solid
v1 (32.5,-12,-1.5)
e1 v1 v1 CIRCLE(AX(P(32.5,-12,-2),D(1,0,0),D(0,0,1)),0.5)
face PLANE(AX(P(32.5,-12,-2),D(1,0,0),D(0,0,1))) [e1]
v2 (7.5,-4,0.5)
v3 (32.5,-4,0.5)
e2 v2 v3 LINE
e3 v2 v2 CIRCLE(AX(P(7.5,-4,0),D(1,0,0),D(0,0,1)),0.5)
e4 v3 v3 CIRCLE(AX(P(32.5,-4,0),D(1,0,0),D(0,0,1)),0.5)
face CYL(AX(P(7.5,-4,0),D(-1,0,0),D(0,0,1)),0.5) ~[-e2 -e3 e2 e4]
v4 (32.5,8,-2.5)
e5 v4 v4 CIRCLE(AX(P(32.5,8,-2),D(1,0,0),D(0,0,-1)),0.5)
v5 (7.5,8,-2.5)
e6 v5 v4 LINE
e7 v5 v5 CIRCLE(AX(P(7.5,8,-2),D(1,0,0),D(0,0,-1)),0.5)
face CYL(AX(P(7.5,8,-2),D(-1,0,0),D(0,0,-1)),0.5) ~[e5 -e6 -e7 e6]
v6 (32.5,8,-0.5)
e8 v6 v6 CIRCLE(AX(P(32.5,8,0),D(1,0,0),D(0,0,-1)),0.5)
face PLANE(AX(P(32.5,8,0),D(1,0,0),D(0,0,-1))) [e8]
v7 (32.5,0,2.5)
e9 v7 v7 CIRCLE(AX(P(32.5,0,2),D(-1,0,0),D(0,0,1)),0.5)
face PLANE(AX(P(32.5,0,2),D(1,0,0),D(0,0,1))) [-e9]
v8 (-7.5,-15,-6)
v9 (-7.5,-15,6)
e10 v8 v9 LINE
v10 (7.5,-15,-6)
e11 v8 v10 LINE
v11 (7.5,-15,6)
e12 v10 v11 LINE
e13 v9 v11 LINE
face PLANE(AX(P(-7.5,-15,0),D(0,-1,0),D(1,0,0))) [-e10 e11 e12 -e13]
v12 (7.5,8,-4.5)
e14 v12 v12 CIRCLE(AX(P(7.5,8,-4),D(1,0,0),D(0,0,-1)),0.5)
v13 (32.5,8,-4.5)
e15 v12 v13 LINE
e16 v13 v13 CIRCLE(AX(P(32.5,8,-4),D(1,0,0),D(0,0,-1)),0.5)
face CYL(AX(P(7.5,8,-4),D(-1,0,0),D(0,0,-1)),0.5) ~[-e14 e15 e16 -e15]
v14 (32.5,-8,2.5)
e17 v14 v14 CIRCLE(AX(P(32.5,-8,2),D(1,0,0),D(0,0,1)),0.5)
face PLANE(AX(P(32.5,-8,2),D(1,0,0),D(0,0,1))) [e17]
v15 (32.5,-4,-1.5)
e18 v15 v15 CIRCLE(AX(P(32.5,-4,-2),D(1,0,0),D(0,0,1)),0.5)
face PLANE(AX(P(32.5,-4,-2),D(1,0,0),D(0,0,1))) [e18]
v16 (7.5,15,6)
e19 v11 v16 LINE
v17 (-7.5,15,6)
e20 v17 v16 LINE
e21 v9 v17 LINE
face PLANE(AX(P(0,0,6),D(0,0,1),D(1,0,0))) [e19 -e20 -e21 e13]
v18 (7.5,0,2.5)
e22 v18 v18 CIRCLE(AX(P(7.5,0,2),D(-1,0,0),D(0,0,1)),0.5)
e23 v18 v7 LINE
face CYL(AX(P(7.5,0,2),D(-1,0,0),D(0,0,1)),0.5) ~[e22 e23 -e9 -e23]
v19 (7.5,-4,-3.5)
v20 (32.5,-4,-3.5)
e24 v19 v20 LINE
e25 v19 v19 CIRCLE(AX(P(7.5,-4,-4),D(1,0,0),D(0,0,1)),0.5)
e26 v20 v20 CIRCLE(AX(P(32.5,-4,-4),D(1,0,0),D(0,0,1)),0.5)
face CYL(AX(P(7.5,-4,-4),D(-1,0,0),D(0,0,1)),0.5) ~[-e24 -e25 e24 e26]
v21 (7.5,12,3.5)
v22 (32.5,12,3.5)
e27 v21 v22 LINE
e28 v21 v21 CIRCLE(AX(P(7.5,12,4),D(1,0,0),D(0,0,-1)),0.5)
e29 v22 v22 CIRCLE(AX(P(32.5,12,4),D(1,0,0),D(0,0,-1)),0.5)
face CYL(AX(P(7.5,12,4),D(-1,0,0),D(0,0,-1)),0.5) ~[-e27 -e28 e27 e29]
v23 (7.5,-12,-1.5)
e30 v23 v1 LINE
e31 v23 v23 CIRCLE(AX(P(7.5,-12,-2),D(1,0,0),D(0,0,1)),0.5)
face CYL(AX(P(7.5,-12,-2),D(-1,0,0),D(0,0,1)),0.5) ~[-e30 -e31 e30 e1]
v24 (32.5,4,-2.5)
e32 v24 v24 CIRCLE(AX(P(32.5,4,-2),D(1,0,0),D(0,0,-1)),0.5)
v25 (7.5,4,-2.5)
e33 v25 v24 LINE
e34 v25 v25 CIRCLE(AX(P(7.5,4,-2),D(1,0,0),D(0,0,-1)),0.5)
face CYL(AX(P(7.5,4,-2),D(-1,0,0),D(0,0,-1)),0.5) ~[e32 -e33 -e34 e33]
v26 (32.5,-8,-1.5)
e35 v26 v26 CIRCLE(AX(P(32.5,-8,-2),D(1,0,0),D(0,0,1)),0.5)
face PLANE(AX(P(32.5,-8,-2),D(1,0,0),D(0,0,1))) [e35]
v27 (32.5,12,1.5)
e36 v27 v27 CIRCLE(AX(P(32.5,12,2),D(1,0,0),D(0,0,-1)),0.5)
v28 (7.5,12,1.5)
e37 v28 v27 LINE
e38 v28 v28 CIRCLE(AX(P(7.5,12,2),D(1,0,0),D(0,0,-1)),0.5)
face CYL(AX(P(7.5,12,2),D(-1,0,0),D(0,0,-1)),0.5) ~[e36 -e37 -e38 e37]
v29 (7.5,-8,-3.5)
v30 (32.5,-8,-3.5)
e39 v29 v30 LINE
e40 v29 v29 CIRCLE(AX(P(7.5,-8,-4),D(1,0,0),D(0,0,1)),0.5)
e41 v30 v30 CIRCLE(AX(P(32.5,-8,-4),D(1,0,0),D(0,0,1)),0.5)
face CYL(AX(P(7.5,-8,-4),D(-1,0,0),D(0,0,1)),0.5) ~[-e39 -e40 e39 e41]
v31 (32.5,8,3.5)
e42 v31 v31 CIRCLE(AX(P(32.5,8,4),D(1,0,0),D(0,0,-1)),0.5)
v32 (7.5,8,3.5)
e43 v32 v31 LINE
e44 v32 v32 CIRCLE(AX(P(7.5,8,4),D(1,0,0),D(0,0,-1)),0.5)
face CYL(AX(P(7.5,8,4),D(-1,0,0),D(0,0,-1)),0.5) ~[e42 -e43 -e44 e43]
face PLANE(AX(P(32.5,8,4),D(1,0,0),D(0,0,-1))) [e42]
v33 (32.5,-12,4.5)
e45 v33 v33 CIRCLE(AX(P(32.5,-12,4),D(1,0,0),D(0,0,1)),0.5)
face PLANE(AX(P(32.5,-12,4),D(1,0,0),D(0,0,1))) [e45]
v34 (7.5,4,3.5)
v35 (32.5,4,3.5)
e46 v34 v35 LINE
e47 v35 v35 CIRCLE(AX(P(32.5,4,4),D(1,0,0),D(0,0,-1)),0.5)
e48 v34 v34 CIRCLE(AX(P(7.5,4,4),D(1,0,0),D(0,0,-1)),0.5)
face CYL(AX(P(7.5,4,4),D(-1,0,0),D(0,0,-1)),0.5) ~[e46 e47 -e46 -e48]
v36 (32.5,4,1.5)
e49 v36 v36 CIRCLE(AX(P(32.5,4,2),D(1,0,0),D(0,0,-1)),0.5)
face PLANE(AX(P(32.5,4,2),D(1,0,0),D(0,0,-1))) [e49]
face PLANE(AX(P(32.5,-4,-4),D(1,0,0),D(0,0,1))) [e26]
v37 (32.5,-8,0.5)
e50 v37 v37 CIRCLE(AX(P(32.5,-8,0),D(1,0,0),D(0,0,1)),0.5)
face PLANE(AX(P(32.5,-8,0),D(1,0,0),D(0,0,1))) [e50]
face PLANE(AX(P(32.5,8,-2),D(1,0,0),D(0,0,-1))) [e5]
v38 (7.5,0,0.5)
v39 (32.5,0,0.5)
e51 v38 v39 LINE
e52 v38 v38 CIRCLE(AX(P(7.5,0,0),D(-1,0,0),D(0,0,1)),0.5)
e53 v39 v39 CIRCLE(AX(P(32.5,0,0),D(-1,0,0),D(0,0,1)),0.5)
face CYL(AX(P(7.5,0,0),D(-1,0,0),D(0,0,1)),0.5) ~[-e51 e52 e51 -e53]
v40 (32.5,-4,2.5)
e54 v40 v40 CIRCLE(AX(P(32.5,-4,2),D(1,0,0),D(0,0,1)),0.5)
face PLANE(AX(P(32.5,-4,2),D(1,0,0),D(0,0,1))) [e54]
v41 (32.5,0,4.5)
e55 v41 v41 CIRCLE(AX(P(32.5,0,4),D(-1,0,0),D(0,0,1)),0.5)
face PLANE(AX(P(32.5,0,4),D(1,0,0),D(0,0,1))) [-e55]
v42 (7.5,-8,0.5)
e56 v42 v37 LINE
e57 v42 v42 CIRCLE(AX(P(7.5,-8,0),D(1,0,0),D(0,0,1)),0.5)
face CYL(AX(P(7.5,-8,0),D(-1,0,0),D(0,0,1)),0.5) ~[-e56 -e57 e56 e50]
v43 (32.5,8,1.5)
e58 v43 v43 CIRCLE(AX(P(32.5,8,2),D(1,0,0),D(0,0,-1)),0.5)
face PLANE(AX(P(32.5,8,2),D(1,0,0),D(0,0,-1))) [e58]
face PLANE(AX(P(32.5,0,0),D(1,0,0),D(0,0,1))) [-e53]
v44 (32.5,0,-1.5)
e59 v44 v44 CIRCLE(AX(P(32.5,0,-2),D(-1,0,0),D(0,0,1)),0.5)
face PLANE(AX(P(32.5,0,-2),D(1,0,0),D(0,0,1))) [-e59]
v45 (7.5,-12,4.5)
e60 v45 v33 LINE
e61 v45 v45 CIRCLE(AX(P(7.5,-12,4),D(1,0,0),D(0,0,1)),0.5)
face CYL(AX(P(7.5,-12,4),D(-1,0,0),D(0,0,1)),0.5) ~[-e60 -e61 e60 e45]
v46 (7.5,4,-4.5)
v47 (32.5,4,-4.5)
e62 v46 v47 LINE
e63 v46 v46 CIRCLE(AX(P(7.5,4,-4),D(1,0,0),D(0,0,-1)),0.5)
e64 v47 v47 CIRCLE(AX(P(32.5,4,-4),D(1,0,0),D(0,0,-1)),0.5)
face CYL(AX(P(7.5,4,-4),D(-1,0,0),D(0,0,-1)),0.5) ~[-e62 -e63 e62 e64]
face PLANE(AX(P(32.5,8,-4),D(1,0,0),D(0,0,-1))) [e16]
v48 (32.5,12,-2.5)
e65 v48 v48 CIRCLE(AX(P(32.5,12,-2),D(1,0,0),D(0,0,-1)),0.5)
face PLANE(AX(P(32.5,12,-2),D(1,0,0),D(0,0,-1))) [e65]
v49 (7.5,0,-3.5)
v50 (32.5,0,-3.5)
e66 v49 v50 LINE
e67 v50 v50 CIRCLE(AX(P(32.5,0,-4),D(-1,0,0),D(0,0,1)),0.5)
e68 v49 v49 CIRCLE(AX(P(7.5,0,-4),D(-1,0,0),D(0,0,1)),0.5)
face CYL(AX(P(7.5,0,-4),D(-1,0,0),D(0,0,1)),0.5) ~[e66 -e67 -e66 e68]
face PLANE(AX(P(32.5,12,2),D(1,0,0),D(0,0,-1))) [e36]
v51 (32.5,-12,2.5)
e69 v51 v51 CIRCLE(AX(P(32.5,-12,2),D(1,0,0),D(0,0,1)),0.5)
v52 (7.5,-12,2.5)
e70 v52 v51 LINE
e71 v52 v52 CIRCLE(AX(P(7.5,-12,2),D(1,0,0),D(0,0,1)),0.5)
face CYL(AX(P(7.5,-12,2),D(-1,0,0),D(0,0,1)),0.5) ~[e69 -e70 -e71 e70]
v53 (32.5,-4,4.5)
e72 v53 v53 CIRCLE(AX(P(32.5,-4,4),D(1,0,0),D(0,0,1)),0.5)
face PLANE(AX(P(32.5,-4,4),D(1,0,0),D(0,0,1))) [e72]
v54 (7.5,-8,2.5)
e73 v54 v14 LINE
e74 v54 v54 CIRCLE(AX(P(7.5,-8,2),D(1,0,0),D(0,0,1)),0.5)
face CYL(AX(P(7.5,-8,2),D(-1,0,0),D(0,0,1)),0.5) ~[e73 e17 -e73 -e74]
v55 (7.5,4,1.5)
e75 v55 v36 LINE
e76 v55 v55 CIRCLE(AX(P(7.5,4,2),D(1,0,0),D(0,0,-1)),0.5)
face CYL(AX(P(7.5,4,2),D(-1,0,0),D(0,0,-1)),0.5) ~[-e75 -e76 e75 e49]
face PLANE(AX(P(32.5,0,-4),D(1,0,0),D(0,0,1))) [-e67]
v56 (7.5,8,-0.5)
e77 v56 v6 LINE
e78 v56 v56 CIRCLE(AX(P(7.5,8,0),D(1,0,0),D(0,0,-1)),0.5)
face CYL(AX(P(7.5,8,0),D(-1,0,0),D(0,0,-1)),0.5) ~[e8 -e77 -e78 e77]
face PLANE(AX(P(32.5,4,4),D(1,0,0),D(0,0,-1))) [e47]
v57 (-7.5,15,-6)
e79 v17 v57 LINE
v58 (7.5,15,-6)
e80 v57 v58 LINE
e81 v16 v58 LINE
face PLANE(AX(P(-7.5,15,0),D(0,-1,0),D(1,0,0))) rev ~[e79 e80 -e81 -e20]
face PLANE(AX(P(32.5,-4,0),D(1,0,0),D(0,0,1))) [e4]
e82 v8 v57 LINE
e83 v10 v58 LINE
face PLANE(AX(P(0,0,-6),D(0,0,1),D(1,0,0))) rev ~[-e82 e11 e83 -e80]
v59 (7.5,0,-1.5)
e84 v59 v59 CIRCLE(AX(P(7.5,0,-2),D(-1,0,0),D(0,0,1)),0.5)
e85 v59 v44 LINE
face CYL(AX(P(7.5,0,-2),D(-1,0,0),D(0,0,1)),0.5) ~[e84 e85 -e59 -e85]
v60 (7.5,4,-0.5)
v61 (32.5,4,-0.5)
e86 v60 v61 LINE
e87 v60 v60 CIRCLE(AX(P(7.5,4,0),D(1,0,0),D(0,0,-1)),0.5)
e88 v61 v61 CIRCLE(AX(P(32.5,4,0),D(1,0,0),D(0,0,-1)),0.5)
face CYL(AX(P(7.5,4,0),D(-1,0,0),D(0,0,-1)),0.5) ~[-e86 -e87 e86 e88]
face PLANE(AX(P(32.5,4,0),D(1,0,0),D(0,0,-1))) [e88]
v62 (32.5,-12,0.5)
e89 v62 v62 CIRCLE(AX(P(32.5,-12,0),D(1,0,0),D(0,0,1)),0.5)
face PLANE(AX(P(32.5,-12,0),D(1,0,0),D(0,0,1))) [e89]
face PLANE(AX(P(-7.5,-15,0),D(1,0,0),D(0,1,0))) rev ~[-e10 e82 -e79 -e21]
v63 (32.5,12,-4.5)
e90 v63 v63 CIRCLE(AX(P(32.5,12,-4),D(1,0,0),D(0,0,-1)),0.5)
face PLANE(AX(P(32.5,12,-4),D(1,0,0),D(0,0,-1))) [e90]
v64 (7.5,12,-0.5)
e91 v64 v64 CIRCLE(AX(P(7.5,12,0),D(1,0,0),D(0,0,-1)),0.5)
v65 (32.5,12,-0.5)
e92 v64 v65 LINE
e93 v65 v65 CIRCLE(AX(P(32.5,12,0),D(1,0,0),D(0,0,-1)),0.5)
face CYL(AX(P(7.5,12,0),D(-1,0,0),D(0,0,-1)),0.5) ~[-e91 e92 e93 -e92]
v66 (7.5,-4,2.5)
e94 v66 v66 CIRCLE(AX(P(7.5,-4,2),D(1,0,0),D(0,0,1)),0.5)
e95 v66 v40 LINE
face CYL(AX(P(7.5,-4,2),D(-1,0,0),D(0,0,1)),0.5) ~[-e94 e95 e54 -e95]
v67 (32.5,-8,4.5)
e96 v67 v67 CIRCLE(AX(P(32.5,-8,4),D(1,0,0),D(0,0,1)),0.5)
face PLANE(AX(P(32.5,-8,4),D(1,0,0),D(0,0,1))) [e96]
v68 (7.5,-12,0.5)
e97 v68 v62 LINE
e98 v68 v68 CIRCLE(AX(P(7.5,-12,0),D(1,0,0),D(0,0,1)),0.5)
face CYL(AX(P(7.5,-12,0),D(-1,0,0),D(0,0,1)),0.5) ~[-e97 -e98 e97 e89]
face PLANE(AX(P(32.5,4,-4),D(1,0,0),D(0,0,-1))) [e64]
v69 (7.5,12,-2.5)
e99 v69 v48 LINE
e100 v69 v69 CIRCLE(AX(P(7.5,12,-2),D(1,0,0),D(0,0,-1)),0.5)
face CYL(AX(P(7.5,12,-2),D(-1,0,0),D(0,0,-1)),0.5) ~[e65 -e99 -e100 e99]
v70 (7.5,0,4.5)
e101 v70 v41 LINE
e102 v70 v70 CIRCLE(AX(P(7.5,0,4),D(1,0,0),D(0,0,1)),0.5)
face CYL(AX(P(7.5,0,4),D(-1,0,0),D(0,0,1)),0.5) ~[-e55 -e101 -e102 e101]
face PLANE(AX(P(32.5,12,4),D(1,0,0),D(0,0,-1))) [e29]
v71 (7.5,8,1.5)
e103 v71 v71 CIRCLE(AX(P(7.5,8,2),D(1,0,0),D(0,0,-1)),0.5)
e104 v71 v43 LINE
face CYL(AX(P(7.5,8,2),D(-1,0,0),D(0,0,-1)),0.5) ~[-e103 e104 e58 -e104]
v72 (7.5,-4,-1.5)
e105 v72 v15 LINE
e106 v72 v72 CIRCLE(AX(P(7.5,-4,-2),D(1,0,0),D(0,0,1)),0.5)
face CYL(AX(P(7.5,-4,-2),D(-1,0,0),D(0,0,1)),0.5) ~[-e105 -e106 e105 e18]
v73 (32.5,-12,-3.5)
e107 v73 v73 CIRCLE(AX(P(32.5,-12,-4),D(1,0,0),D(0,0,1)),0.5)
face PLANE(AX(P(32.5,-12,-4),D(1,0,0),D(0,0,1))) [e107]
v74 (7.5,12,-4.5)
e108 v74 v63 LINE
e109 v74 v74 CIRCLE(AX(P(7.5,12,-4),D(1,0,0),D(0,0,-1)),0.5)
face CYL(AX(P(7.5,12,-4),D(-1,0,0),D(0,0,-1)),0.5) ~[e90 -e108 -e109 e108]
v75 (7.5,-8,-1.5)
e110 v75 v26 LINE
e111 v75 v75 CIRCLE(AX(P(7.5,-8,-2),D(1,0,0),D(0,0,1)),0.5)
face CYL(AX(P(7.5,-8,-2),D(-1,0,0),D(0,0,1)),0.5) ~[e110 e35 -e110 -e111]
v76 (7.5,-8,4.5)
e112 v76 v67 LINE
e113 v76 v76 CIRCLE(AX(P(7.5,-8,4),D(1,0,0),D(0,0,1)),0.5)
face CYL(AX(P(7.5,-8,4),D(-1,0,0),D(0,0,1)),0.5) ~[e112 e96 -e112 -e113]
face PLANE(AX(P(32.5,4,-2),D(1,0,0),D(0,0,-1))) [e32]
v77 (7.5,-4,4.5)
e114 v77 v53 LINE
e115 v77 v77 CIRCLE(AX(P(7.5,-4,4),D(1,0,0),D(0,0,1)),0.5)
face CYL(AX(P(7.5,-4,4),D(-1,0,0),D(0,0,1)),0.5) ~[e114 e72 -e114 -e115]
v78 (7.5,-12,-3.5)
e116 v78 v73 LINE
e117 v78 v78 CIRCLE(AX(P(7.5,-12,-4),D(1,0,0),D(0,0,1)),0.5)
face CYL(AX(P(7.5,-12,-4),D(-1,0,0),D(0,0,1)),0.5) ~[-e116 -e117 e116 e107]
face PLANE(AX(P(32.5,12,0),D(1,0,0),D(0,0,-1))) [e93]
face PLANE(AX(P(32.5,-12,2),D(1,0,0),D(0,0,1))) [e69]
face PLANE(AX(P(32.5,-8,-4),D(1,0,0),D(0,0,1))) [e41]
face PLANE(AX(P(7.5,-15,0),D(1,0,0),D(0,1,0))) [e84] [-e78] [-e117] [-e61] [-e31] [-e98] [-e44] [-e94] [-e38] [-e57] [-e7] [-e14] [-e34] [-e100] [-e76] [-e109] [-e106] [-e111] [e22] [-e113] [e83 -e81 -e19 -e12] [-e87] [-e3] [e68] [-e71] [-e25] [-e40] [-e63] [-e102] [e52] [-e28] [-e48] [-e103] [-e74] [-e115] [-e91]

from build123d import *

# Parameters (mm, degrees)
SKETCH_1_W               = 15
SKETCH_1_H               = 30
EXTRUDE_1_DEPTH          = 6
SKETCH_2_R               = 0.5
EXTRUDE_2_DEPTH          = 25
PATTERN_LINEAR_1_COUNT   = 4
PATTERN_LINEAR_1_PITCH   = 4
MIRROR_1_COPY_1_SKETCH_R = 0.5
MIRROR_1_COPY_1_DEPTH    = 25
MIRROR_1_COPY_2_SKETCH_R = 0.5
MIRROR_1_COPY_2_DEPTH    = 25
MIRROR_1_COPY_3_SKETCH_R = 0.5
MIRROR_1_COPY_3_DEPTH    = 25
MIRROR_1_COPY_4_SKETCH_R = 0.5
MIRROR_1_COPY_4_DEPTH    = 25


with BuildPart() as part:
    # 草图1 → 凸台-拉伸1 (new, symmetric)
    with BuildSketch(Plane.XY):
        Rectangle(SKETCH_1_W, SKETCH_1_H)
    extrude(amount=EXTRUDE_1_DEPTH, both=True)

    # 草图2 → 凸台-拉伸2 (add)
    with BuildSketch(Plane(origin=(7.5, 0, 0), x_dir=(0, 0, -1), z_dir=(1, 0, 0))):
        with Locations(Location((-4, 0, 0), (0, 0, 180))):
            Circle(SKETCH_2_R)
        with Locations(Location((-2, 0, 0), (0, 0, 180))):
            Circle(SKETCH_2_R)
        with Locations(Location((0, 0, 0), (0, 0, 180))):
            Circle(SKETCH_2_R)
        with Locations(Location((2, 0, 0), (0, 0, 180))):
            Circle(SKETCH_2_R)
        with Locations(Location((4, 0, 0), (0, 0, 180))):
            Circle(SKETCH_2_R)
    extrude_2 = extrude(amount=EXTRUDE_2_DEPTH)

    # 阵列(线性)1: 凸台-拉伸2 ×4
    with Locations(*[(0, -i * PATTERN_LINEAR_1_PITCH, 0) for i in range(1, PATTERN_LINEAR_1_COUNT)]):
        add(extrude_2)

    # 镜向1 copy 1 sketch → 镜向1 copy 1 (add)
    with BuildSketch(Plane(origin=(7.5, 4, 0), x_dir=(0, 0, -1), z_dir=(1, 0, 0))):
        with Locations((-4, 0)):
            Circle(MIRROR_1_COPY_1_SKETCH_R)
        with Locations((-2, 0)):
            Circle(MIRROR_1_COPY_1_SKETCH_R)
        Circle(MIRROR_1_COPY_1_SKETCH_R)
        with Locations((2, 0)):
            Circle(MIRROR_1_COPY_1_SKETCH_R)
        with Locations((4, 0)):
            Circle(MIRROR_1_COPY_1_SKETCH_R)
    extrude(amount=MIRROR_1_COPY_1_DEPTH)

    # 镜向1 copy 2 sketch → 镜向1 copy 2 (add)
    with BuildSketch(Plane(origin=(7.5, 8, 0), x_dir=(0, 0, -1), z_dir=(1, 0, 0))):
        with Locations((-4, 0)):
            Circle(MIRROR_1_COPY_2_SKETCH_R)
        with Locations((-2, 0)):
            Circle(MIRROR_1_COPY_2_SKETCH_R)
        Circle(MIRROR_1_COPY_2_SKETCH_R)
        with Locations((2, 0)):
            Circle(MIRROR_1_COPY_2_SKETCH_R)
        with Locations((4, 0)):
            Circle(MIRROR_1_COPY_2_SKETCH_R)
    extrude(amount=MIRROR_1_COPY_2_DEPTH)

    # 镜向1 copy 3 sketch → 镜向1 copy 3 (add)
    with BuildSketch(Plane(origin=(7.5, 12, 0), x_dir=(0, 0, -1), z_dir=(1, 0, 0))):
        with Locations((-4, 0)):
            Circle(MIRROR_1_COPY_3_SKETCH_R)
        with Locations((-2, 0)):
            Circle(MIRROR_1_COPY_3_SKETCH_R)
        Circle(MIRROR_1_COPY_3_SKETCH_R)
        with Locations((2, 0)):
            Circle(MIRROR_1_COPY_3_SKETCH_R)
        with Locations((4, 0)):
            Circle(MIRROR_1_COPY_3_SKETCH_R)
    extrude(amount=MIRROR_1_COPY_3_DEPTH)

    # 镜向1 copy 4 sketch → 镜向1 copy 4 (add)
    with BuildSketch(Plane(origin=(7.5, 0, 0), x_dir=(0, 0, -1), z_dir=(1, 0, 0))):
        with Locations((-4, 0)):
            Circle(MIRROR_1_COPY_4_SKETCH_R)
        with Locations((-2, 0)):
            Circle(MIRROR_1_COPY_4_SKETCH_R)
        Circle(MIRROR_1_COPY_4_SKETCH_R)
        with Locations((2, 0)):
            Circle(MIRROR_1_COPY_4_SKETCH_R)
        with Locations((4, 0)):
            Circle(MIRROR_1_COPY_4_SKETCH_R)
    extrude(amount=MIRROR_1_COPY_4_DEPTH)


solid = part.part
